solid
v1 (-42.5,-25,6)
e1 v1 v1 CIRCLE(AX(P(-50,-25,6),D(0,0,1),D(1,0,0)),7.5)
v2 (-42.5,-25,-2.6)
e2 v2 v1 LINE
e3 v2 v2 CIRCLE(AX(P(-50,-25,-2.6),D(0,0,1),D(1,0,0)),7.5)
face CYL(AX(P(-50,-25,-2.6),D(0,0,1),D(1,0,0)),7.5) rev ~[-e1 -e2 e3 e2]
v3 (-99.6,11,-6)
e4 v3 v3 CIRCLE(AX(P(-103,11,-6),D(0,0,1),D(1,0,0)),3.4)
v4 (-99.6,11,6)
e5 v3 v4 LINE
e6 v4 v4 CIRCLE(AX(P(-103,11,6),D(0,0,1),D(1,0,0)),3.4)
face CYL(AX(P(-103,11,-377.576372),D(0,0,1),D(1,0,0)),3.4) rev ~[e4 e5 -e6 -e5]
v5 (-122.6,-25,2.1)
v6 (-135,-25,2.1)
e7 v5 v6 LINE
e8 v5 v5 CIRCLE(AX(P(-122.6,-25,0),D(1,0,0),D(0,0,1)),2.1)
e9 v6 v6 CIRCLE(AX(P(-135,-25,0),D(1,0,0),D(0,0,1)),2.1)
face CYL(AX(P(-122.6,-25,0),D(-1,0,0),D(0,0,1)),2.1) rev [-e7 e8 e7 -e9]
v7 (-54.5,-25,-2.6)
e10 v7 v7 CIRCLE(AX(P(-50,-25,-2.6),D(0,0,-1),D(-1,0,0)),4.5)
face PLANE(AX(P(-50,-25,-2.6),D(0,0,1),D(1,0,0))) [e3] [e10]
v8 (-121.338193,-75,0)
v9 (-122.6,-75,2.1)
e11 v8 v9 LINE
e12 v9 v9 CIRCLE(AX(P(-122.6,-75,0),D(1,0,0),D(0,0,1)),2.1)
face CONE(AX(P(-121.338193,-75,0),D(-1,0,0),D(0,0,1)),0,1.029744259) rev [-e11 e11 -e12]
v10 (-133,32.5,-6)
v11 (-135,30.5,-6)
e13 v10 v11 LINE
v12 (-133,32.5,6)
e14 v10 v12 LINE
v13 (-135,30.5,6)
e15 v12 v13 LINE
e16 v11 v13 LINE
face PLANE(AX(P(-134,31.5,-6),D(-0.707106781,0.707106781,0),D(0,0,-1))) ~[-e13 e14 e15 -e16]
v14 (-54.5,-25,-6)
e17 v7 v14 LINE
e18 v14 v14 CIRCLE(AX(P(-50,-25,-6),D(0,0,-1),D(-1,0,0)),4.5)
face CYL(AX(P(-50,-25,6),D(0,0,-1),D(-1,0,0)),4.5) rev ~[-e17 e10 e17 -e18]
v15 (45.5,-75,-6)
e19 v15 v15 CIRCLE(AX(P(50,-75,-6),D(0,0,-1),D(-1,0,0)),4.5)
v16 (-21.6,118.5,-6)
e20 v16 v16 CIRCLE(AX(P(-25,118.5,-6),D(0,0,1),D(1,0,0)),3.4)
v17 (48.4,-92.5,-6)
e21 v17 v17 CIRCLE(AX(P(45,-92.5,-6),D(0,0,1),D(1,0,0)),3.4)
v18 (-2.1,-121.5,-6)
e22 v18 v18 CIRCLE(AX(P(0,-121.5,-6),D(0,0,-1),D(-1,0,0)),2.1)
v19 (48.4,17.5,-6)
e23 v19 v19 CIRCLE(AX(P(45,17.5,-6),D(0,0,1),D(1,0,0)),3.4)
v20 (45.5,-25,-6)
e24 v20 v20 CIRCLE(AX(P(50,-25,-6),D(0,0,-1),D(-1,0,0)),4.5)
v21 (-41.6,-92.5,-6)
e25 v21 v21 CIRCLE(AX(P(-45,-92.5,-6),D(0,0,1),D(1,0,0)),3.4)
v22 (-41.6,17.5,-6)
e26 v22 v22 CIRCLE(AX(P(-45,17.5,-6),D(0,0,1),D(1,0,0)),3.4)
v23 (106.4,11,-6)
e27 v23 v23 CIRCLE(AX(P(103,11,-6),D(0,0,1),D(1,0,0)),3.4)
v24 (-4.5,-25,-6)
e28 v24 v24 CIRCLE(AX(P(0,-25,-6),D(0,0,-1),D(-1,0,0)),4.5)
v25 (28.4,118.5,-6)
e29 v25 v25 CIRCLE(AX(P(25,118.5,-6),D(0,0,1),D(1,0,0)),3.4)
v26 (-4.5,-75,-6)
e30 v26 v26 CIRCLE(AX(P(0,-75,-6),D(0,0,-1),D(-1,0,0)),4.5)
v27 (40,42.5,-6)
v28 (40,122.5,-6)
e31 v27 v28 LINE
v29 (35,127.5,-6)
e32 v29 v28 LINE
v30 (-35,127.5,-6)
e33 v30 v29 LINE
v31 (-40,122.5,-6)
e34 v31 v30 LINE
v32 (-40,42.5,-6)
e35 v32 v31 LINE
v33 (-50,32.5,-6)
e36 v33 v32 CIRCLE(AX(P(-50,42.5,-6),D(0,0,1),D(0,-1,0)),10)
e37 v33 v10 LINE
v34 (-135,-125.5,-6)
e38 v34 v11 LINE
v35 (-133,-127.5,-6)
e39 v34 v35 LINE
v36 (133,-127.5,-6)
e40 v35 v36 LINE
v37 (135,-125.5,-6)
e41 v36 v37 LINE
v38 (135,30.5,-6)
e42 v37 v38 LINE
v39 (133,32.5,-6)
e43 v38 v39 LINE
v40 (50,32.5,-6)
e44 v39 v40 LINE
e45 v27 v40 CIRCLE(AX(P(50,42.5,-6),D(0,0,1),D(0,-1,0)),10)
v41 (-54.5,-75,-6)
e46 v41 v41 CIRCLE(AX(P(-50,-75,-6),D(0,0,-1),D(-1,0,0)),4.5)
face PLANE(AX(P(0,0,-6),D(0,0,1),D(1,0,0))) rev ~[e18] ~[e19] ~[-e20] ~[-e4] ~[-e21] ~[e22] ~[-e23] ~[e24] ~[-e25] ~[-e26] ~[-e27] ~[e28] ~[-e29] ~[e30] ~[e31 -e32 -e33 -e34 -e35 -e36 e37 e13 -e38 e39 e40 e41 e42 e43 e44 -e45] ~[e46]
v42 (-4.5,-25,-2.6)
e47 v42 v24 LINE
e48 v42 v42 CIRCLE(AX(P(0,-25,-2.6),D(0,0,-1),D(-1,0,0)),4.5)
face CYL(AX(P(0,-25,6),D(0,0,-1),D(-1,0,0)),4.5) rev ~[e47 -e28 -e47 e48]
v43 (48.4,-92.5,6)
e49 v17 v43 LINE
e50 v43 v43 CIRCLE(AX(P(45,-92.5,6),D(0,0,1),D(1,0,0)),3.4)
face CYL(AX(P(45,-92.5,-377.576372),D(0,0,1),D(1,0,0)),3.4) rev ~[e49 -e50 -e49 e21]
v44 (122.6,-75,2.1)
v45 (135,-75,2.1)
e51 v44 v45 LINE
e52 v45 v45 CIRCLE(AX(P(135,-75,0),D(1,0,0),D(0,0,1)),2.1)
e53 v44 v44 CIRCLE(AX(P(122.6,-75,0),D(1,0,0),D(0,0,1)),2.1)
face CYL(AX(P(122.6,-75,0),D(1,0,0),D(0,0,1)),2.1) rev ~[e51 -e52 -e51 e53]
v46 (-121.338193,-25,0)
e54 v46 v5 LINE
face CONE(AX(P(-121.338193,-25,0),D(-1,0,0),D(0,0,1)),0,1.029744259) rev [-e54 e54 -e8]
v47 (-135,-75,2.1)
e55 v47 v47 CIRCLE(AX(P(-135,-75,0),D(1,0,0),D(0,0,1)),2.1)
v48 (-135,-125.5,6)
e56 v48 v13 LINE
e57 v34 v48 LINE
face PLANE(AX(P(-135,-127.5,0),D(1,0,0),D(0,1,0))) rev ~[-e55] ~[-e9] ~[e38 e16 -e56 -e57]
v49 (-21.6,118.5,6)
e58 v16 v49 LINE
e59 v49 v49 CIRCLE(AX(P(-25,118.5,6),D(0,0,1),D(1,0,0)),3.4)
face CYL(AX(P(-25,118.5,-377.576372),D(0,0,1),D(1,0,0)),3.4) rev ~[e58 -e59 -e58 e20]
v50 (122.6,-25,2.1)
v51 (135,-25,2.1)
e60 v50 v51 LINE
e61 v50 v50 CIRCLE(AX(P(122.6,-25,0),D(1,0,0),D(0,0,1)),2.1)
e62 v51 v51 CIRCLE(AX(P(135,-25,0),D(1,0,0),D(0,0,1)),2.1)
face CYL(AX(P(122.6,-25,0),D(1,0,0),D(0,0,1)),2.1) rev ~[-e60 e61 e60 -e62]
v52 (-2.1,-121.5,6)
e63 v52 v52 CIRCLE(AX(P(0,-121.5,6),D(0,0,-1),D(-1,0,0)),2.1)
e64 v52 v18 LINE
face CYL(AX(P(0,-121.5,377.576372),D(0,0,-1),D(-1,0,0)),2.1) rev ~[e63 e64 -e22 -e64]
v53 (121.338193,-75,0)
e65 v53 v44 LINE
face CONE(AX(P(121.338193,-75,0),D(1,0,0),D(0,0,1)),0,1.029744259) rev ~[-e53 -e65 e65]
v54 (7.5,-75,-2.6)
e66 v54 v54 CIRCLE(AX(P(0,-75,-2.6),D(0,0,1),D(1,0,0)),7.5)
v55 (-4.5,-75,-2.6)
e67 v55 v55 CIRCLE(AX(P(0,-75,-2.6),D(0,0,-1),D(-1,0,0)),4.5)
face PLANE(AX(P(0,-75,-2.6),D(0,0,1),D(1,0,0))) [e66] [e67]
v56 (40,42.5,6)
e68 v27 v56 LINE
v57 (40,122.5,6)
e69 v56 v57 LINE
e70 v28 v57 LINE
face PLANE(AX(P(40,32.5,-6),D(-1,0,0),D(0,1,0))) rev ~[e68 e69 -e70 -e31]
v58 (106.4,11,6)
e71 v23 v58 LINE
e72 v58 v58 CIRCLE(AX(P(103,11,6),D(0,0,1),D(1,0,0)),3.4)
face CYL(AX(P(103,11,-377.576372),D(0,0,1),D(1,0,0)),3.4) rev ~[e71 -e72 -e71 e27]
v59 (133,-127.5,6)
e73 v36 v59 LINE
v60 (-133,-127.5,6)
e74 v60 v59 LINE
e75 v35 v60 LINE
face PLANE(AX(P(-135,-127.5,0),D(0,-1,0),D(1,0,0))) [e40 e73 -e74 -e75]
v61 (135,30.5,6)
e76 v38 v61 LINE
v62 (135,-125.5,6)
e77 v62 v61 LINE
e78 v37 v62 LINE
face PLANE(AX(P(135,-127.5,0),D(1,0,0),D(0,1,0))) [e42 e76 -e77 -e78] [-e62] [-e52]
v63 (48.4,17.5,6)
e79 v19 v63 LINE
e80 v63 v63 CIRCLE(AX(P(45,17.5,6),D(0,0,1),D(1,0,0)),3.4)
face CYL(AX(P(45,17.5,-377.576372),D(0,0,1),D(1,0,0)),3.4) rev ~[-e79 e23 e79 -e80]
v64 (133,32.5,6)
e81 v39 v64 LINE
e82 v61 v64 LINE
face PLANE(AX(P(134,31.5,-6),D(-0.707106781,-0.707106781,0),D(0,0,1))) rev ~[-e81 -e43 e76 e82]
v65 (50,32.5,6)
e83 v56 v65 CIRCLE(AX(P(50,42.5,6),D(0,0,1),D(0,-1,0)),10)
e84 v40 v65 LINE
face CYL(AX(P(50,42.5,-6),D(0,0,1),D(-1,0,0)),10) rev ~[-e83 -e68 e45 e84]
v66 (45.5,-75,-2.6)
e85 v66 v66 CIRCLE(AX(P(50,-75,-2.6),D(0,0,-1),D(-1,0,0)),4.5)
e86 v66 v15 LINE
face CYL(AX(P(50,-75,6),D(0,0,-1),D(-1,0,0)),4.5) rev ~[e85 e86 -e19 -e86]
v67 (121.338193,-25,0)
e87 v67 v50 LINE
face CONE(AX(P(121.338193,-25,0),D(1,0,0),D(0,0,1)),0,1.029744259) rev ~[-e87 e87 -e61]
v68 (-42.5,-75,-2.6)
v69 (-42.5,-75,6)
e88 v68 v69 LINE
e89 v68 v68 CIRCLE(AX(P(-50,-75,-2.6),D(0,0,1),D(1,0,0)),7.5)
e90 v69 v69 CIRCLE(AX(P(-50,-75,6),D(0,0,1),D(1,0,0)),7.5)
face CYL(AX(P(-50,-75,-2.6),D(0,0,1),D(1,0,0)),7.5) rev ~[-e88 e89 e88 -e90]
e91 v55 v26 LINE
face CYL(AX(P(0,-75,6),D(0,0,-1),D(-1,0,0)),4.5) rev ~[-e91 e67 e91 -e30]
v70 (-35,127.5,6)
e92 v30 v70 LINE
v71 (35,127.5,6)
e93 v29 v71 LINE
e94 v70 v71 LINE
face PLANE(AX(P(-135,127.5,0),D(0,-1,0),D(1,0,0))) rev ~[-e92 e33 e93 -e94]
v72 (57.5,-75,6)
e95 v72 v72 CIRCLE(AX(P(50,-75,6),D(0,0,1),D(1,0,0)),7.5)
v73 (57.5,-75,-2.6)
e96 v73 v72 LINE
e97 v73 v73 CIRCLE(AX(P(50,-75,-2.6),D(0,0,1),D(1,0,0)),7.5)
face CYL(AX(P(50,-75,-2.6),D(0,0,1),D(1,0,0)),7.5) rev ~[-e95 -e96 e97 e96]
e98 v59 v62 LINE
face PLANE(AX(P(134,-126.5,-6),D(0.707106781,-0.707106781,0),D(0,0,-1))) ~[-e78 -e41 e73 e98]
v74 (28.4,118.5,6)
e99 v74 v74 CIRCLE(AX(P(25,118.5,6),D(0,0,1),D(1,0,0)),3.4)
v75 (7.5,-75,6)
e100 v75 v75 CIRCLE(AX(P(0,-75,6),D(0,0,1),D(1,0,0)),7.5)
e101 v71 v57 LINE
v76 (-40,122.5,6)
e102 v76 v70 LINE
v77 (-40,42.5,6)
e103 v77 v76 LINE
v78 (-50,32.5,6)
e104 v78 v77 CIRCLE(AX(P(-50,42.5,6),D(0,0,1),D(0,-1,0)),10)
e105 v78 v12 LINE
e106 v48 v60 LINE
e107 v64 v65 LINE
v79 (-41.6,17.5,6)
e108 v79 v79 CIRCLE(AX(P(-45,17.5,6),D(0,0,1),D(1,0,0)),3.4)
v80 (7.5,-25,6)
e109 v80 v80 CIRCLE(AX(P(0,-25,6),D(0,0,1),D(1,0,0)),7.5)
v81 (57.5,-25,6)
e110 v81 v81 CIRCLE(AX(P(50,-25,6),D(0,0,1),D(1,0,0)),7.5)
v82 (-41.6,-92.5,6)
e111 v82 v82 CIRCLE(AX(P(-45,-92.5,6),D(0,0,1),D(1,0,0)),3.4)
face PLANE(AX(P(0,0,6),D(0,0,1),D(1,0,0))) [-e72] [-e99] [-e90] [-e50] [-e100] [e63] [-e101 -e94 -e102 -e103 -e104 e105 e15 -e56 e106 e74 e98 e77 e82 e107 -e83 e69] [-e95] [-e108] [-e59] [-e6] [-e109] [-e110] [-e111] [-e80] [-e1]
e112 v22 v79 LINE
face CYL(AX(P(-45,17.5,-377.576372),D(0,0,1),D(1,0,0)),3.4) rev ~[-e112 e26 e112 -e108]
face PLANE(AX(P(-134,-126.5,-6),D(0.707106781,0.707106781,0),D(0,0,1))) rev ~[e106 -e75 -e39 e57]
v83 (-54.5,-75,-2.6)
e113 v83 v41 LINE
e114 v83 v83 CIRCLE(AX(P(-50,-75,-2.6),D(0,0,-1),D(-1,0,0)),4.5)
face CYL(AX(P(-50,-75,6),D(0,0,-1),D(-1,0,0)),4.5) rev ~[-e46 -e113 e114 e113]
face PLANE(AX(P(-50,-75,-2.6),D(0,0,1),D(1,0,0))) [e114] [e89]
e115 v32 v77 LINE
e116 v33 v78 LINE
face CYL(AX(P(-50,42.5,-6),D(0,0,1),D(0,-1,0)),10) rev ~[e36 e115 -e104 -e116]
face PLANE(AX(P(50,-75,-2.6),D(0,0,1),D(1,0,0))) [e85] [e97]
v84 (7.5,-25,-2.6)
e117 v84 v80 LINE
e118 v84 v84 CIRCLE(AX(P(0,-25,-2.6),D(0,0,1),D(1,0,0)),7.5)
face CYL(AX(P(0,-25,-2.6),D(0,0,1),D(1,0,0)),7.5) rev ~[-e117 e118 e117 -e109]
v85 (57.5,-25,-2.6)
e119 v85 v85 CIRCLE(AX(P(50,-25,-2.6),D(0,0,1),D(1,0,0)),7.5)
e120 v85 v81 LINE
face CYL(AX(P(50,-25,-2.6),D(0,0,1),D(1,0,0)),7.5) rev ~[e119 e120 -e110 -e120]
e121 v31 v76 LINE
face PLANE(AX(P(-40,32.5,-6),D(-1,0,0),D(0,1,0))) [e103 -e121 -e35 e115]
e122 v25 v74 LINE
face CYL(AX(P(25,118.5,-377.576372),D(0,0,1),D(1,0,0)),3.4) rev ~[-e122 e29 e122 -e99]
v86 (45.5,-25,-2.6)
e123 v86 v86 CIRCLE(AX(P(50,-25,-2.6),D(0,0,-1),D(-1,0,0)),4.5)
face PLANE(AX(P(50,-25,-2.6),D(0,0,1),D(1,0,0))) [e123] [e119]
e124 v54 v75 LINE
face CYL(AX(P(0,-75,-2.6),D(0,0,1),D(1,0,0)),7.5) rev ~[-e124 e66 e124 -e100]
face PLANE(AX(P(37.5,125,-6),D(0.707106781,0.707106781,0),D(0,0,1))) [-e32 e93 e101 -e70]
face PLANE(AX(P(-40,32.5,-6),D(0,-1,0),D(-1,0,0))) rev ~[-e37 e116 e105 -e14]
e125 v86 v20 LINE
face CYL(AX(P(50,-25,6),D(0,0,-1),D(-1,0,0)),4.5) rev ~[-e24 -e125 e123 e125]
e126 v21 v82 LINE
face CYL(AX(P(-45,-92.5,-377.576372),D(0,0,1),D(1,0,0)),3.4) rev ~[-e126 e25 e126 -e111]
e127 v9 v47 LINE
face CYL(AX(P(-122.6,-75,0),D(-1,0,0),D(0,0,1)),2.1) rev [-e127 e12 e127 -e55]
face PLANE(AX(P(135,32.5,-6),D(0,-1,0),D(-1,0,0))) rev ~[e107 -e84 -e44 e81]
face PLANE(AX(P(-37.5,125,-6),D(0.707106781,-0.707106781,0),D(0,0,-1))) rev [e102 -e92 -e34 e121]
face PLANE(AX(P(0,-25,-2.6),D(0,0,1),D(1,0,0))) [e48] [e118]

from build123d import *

# Parameters (mm, degrees)
SKETCH_1_W                     = 270
SKETCH_1_H                     = 255
EXTRUDE_1_DEPTH                = 6
SKETCH_2_W                     = 95
SKETCH_2_H                     = 95
CUT_EXTRUDE_1_DEPTH            = 12
HOLE_WIZARD_M8_1_D             = 6.8
HOLE_WIZARD_M8_2_D             = 6.8
CHAMFER_1_SIZE                 = 5
CHAMFER_2_SIZE                 = 2
HOLE_WIZARD_M8_2_2_D           = 9
HOLE_WIZARD_M8_2_2_CBORE_D     = 15
HOLE_WIZARD_M8_2_2_CBORE_DEPTH = 8.6
FILLET_1_R                     = 10
HOLE_WIZARD_M5_3_AT_2_COUNT    = 2
HOLE_WIZARD_M5_3_AT_2_PITCH    = 50
HOLE_WIZARD_M5_4_D             = 4.2


with BuildPart() as part:
    # 草图1 → 凸台-拉伸1 (new, symmetric)
    with BuildSketch(Plane.XY):
        Rectangle(SKETCH_1_W, SKETCH_1_H)
    extrude(amount=EXTRUDE_1_DEPTH, both=True)

    # 草图2 → 切除-拉伸1 (cut)
    with BuildSketch(Plane(origin=(0, 0, -6), x_dir=(-1, 0, 0), z_dir=(0, 0, -1))):
        with Locations((87.5, 80)):
            Rectangle(SKETCH_2_W, SKETCH_2_H)
        with Locations((-87.5, 80)):
            Rectangle(SKETCH_2_W, SKETCH_2_H)
    extrude(amount=-CUT_EXTRUDE_1_DEPTH, mode=Mode.SUBTRACT)

    # Hole Wizard M8 _1 (through all)
    with Locations(Plane(origin=(0, 0, -6), x_dir=(-1, 0, 0), z_dir=(0, 0, -1))):
        with Locations((-25, 118.5), (25, 118.5)):
            Hole(HOLE_WIZARD_M8_1_D / 2)

    # Hole Wizard M8 _2 (through all)
    with Locations(Plane(origin=(0, 0, -6), x_dir=(-1, 0, 0), z_dir=(0, 0, -1))):
        with Locations((-45, -92.5), (45, -92.5), (-45, 17.5), (45, 17.5), (-103, 11), (103, 11)):
            Hole(HOLE_WIZARD_M8_2_D / 2)

    # 倒角1
    chamfer_1_edges = [part.edges().sort_by_distance(p)[0] for p in [
        (-40, 127.5, 0),
        (40, 127.5, 0),
    ]]
    chamfer(chamfer_1_edges, length=CHAMFER_1_SIZE)

    # 倒角2
    chamfer_2_edges = [part.edges().sort_by_distance(p)[0] for p in [
        (-135, 32.5, 0),
        (135, 32.5, 0),
        (135, -127.5, 0),
        (-135, -127.5, 0),
    ]]
    chamfer(chamfer_2_edges, length=CHAMFER_2_SIZE)

    # Hole Wizard M8 _2 2 (through all)
    with Locations(Plane.XY.offset(6)):
        with Locations((-50, -25), (-50, -75), (0, -25), (0, -75), (50, -25), (50, -75)):
            CounterBoreHole(HOLE_WIZARD_M8_2_2_D / 2, HOLE_WIZARD_M8_2_2_CBORE_D / 2, HOLE_WIZARD_M8_2_2_CBORE_DEPTH)

    # 圆角1
    fillet_1_edges = [part.edges().sort_by_distance(p)[0] for p in [
        (-40, 32.5, 0),
        (40, 32.5, 0),
    ]]
    fillet(fillet_1_edges, radius=FILLET_1_R)

    # 草图24 → M5 螺纹孔3 (revolve, cut)
    with BuildSketch(Plane(origin=(-135, -75, 0), x_dir=(0, 0, 1), z_dir=(0, 1, 0))):
        Polygon((0, 0), (0, 13.6618073), (2.1, 12.4), (2.1, 0), align=None)
    hole_wizard_m5_3 = revolve(axis=Axis((-141.35, -75, 0), (1, 0, 0)), mode=Mode.SUBTRACT)

    # M5 螺纹孔3 at 2: M5 螺纹孔3 ×2
    with Locations(*[(0, i * HOLE_WIZARD_M5_3_AT_2_PITCH, 0) for i in range(1, HOLE_WIZARD_M5_3_AT_2_COUNT)]):
        add(hole_wizard_m5_3, mode=Mode.SUBTRACT)

    # 镜向1: M5 螺纹孔3 across plane
    add(hole_wizard_m5_3.mirror(Plane.ZY), mode=Mode.SUBTRACT)

    # 镜向1 copy 1 sketch → 镜向1 copy 1 (revolve, cut)
    with BuildSketch(Plane(origin=(135, -25, 0), x_dir=(0, 0, 1), z_dir=(0, 1, 0))):
        Polygon((0, 0), (0, -13.6618073), (2.1, -12.4), (2.1, 0), align=None)
    revolve(axis=Axis((141.35, -25, 0), (1, 0, 0)), mode=Mode.SUBTRACT)

    # M5 螺纹孔4 (through all)
    with Locations(Plane.XY.offset(6)):
        with Locations((0, -121.5)):
            Hole(HOLE_WIZARD_M5_4_D / 2)


solid = part.part
